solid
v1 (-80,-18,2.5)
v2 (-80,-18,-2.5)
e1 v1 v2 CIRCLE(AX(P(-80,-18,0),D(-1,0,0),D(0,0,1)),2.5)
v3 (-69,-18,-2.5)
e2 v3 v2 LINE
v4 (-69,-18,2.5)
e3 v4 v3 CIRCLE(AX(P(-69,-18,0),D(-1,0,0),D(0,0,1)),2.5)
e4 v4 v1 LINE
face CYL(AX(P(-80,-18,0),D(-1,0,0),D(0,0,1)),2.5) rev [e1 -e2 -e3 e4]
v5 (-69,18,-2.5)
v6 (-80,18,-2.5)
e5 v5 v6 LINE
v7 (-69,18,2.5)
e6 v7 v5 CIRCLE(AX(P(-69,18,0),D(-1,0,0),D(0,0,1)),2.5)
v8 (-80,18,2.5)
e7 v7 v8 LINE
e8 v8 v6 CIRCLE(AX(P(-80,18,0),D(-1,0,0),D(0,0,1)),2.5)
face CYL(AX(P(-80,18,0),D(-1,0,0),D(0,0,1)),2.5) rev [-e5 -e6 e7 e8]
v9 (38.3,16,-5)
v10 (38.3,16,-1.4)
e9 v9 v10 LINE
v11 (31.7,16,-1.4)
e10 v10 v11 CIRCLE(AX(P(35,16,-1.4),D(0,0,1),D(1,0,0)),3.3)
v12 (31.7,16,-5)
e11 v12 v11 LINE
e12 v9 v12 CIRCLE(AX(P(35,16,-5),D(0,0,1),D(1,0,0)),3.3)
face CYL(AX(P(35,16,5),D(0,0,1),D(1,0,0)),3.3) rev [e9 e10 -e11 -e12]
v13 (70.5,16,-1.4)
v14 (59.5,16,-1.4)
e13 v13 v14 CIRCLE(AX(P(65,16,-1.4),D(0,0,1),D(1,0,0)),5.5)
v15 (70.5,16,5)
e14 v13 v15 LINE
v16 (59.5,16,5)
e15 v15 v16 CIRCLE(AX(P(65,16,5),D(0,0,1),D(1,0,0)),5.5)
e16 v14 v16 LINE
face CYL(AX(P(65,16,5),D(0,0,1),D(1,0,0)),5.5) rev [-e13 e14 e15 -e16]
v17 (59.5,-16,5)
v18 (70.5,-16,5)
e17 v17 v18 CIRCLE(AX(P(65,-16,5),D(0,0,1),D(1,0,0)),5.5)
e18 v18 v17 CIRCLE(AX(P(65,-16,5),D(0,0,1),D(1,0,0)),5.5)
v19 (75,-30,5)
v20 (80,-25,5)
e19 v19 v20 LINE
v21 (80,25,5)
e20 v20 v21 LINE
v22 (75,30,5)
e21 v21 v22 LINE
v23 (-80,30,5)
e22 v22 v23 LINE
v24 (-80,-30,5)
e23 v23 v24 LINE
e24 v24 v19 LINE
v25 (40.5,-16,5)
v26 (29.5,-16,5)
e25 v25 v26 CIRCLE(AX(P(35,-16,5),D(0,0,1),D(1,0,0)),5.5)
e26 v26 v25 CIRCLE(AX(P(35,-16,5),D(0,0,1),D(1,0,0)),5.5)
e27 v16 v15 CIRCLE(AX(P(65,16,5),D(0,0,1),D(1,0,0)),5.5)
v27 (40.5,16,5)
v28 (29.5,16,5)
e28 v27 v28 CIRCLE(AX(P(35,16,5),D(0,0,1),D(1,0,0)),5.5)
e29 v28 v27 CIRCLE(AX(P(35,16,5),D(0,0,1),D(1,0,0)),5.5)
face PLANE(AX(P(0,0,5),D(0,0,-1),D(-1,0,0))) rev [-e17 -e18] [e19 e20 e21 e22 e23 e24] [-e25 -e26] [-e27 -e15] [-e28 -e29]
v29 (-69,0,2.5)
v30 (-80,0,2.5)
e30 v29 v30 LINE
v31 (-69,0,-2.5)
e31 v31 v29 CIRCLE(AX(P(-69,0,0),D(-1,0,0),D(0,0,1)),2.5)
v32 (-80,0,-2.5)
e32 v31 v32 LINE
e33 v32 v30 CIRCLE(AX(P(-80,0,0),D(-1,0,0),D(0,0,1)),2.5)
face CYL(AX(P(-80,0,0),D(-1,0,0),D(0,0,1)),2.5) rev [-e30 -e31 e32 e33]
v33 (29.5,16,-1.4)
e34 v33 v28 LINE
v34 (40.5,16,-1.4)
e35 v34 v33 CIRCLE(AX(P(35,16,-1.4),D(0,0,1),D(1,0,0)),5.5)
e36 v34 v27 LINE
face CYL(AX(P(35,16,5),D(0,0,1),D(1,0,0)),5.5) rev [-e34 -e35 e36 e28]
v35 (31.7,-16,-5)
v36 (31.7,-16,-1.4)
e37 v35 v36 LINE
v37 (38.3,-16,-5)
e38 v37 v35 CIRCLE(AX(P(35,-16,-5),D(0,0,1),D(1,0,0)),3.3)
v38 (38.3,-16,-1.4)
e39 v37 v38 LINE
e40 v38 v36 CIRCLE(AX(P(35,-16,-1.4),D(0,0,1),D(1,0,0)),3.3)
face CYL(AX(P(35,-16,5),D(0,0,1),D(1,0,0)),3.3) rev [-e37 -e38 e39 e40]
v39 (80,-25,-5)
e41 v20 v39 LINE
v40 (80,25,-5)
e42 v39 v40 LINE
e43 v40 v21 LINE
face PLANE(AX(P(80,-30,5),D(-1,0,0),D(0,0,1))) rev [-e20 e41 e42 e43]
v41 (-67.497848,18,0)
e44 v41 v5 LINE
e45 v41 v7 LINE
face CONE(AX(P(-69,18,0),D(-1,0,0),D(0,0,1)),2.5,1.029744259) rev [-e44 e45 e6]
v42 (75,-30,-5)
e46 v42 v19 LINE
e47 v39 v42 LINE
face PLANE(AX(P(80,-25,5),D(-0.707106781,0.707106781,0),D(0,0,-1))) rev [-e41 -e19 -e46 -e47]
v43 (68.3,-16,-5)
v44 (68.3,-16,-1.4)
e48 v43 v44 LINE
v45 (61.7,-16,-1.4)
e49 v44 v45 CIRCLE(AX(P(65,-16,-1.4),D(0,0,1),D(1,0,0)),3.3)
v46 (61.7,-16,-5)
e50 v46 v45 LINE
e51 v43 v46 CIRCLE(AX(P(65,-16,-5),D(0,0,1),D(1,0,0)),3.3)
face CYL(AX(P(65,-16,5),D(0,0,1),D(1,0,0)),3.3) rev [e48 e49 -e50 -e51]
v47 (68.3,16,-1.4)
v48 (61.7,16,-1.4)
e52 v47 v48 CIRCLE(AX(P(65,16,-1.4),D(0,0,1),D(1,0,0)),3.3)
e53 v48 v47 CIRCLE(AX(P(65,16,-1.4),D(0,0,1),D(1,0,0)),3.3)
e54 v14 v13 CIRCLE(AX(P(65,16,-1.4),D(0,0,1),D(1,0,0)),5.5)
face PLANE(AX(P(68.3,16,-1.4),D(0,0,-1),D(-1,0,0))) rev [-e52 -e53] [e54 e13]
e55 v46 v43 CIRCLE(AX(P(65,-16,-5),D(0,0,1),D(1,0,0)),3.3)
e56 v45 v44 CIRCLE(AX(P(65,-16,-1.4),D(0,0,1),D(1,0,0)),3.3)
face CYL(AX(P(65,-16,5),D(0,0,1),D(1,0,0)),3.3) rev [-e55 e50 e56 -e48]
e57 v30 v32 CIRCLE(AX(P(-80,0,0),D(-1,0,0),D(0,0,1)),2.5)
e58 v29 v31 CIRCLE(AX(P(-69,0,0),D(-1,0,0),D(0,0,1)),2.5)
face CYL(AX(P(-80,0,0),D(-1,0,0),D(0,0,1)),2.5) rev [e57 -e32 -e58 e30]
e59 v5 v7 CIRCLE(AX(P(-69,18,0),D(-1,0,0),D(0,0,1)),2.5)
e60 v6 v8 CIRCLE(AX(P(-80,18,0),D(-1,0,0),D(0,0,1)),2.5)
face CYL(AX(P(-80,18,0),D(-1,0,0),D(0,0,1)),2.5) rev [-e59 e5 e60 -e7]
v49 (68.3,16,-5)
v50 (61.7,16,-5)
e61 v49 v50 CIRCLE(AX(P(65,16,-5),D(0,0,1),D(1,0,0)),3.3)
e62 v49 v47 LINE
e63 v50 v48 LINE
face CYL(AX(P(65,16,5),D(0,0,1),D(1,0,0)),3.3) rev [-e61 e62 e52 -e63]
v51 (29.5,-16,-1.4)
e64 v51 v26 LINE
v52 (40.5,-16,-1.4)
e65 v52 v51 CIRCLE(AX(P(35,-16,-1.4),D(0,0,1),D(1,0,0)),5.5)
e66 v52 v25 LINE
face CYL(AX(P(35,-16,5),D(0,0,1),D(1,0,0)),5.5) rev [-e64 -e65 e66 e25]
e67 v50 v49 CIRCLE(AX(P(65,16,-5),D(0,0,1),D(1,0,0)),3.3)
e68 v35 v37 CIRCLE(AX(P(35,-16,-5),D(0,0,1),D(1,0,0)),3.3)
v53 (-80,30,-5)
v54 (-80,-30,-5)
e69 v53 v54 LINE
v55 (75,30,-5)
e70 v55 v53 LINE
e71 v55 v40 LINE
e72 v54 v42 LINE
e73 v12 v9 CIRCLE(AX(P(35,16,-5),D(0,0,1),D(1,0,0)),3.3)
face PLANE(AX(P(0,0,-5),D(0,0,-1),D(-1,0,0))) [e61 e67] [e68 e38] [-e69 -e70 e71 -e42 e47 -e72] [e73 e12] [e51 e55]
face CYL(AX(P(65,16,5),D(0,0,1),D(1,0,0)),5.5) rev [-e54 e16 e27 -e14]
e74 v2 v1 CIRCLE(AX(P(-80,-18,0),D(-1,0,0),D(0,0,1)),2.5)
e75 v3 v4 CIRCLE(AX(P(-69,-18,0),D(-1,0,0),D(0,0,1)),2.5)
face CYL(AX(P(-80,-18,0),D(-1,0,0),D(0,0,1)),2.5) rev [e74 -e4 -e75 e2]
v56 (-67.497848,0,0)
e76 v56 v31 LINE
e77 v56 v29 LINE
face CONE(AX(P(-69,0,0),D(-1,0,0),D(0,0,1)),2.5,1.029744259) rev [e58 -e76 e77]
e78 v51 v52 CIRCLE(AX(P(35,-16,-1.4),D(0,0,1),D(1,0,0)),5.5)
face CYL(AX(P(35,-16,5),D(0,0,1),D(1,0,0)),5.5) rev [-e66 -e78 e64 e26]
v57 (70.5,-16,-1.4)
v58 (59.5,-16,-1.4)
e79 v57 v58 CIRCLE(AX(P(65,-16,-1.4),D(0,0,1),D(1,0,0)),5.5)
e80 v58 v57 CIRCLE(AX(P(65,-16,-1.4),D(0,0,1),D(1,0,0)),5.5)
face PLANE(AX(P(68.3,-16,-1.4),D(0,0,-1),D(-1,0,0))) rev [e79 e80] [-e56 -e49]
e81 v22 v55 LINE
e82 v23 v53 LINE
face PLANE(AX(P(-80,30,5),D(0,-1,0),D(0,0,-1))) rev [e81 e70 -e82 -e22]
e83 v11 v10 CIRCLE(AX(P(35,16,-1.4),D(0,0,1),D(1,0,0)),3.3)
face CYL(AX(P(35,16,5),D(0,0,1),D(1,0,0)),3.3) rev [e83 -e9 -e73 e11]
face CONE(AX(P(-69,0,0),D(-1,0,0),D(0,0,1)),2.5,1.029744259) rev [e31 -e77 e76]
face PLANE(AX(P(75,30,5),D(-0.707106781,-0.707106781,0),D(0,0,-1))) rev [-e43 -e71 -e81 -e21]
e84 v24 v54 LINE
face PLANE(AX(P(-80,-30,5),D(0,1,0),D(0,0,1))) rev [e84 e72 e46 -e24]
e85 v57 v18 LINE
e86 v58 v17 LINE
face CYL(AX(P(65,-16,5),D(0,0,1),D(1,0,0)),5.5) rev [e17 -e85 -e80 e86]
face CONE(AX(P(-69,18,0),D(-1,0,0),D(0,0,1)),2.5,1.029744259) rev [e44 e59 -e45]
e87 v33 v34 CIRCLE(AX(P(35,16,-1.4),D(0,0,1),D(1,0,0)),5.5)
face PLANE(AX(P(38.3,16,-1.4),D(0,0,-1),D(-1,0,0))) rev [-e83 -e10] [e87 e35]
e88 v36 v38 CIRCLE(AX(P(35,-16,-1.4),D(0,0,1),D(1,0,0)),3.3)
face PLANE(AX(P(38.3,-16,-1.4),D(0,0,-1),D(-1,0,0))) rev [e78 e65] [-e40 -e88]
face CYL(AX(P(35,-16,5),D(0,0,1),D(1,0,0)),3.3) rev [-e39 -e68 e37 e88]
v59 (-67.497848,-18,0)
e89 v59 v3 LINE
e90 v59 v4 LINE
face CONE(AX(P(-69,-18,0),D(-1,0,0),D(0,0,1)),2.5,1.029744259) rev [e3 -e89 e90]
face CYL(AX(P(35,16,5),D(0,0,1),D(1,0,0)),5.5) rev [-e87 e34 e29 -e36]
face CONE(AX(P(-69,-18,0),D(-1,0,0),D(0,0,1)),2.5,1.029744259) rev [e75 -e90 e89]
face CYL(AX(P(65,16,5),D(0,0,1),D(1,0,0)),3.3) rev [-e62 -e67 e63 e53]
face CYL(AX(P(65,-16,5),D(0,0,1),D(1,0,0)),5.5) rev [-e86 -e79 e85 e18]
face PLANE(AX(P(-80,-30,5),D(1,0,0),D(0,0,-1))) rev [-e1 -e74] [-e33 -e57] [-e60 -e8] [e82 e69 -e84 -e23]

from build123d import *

# Parameters (mm, degrees)
SKETCH1_W                                           = 160
SKETCH1_H                                           = 60
BOSS_EXTRUDE1_DEPTH                                 = 5
CBORE_FOR_M6_HEX_SOCKET_HEAD_CAP_SCREW1_D           = 6.6
CBORE_FOR_M6_HEX_SOCKET_HEAD_CAP_SCREW1_CBORE_D     = 11
CBORE_FOR_M6_HEX_SOCKET_HEAD_CAP_SCREW1_CBORE_DEPTH = 6.4
CHAMFER1_SIZE                                       = 5
M6_TAPPED_HOLE1_D                                   = 5
M6_TAPPED_HOLE1_DEPTH                               = 11
M6_TAPPED_HOLE1_TIP                                 = 1.502151548


with BuildPart() as part:
    # Sketch1 → Boss-Extrude1 (new, symmetric)
    with BuildSketch(Plane.XY):
        Rectangle(SKETCH1_W, SKETCH1_H)
    extrude(amount=BOSS_EXTRUDE1_DEPTH, both=True)

    # CBORE for M6 Hex Socket Head Cap Screw1 (through all)
    with Locations(Plane.XY.offset(5)):
        with Locations((35, -16), (65, -16), (65, 16), (35, 16)):
            CounterBoreHole(CBORE_FOR_M6_HEX_SOCKET_HEAD_CAP_SCREW1_D / 2, CBORE_FOR_M6_HEX_SOCKET_HEAD_CAP_SCREW1_CBORE_D / 2, CBORE_FOR_M6_HEX_SOCKET_HEAD_CAP_SCREW1_CBORE_DEPTH)

    # Chamfer1
    chamfer1_edges = [part.edges().sort_by_distance(p)[0] for p in [
        (80, -30, 0),
        (80, 30, 0),
    ]]
    chamfer(chamfer1_edges, length=CHAMFER1_SIZE)

    # M6 Tapped Hole1
    with Locations(Plane.ZY.offset(80)):
        with Locations((0, 18), (0, 0), (0, -18)):
            Hole(M6_TAPPED_HOLE1_D / 2, depth=M6_TAPPED_HOLE1_DEPTH)
            with Locations((0, 0, -(M6_TAPPED_HOLE1_DEPTH + M6_TAPPED_HOLE1_TIP / 2))):  # 118° drill point
                Cone(0, M6_TAPPED_HOLE1_D / 2, M6_TAPPED_HOLE1_TIP, mode=Mode.SUBTRACT)


solid = part.part
